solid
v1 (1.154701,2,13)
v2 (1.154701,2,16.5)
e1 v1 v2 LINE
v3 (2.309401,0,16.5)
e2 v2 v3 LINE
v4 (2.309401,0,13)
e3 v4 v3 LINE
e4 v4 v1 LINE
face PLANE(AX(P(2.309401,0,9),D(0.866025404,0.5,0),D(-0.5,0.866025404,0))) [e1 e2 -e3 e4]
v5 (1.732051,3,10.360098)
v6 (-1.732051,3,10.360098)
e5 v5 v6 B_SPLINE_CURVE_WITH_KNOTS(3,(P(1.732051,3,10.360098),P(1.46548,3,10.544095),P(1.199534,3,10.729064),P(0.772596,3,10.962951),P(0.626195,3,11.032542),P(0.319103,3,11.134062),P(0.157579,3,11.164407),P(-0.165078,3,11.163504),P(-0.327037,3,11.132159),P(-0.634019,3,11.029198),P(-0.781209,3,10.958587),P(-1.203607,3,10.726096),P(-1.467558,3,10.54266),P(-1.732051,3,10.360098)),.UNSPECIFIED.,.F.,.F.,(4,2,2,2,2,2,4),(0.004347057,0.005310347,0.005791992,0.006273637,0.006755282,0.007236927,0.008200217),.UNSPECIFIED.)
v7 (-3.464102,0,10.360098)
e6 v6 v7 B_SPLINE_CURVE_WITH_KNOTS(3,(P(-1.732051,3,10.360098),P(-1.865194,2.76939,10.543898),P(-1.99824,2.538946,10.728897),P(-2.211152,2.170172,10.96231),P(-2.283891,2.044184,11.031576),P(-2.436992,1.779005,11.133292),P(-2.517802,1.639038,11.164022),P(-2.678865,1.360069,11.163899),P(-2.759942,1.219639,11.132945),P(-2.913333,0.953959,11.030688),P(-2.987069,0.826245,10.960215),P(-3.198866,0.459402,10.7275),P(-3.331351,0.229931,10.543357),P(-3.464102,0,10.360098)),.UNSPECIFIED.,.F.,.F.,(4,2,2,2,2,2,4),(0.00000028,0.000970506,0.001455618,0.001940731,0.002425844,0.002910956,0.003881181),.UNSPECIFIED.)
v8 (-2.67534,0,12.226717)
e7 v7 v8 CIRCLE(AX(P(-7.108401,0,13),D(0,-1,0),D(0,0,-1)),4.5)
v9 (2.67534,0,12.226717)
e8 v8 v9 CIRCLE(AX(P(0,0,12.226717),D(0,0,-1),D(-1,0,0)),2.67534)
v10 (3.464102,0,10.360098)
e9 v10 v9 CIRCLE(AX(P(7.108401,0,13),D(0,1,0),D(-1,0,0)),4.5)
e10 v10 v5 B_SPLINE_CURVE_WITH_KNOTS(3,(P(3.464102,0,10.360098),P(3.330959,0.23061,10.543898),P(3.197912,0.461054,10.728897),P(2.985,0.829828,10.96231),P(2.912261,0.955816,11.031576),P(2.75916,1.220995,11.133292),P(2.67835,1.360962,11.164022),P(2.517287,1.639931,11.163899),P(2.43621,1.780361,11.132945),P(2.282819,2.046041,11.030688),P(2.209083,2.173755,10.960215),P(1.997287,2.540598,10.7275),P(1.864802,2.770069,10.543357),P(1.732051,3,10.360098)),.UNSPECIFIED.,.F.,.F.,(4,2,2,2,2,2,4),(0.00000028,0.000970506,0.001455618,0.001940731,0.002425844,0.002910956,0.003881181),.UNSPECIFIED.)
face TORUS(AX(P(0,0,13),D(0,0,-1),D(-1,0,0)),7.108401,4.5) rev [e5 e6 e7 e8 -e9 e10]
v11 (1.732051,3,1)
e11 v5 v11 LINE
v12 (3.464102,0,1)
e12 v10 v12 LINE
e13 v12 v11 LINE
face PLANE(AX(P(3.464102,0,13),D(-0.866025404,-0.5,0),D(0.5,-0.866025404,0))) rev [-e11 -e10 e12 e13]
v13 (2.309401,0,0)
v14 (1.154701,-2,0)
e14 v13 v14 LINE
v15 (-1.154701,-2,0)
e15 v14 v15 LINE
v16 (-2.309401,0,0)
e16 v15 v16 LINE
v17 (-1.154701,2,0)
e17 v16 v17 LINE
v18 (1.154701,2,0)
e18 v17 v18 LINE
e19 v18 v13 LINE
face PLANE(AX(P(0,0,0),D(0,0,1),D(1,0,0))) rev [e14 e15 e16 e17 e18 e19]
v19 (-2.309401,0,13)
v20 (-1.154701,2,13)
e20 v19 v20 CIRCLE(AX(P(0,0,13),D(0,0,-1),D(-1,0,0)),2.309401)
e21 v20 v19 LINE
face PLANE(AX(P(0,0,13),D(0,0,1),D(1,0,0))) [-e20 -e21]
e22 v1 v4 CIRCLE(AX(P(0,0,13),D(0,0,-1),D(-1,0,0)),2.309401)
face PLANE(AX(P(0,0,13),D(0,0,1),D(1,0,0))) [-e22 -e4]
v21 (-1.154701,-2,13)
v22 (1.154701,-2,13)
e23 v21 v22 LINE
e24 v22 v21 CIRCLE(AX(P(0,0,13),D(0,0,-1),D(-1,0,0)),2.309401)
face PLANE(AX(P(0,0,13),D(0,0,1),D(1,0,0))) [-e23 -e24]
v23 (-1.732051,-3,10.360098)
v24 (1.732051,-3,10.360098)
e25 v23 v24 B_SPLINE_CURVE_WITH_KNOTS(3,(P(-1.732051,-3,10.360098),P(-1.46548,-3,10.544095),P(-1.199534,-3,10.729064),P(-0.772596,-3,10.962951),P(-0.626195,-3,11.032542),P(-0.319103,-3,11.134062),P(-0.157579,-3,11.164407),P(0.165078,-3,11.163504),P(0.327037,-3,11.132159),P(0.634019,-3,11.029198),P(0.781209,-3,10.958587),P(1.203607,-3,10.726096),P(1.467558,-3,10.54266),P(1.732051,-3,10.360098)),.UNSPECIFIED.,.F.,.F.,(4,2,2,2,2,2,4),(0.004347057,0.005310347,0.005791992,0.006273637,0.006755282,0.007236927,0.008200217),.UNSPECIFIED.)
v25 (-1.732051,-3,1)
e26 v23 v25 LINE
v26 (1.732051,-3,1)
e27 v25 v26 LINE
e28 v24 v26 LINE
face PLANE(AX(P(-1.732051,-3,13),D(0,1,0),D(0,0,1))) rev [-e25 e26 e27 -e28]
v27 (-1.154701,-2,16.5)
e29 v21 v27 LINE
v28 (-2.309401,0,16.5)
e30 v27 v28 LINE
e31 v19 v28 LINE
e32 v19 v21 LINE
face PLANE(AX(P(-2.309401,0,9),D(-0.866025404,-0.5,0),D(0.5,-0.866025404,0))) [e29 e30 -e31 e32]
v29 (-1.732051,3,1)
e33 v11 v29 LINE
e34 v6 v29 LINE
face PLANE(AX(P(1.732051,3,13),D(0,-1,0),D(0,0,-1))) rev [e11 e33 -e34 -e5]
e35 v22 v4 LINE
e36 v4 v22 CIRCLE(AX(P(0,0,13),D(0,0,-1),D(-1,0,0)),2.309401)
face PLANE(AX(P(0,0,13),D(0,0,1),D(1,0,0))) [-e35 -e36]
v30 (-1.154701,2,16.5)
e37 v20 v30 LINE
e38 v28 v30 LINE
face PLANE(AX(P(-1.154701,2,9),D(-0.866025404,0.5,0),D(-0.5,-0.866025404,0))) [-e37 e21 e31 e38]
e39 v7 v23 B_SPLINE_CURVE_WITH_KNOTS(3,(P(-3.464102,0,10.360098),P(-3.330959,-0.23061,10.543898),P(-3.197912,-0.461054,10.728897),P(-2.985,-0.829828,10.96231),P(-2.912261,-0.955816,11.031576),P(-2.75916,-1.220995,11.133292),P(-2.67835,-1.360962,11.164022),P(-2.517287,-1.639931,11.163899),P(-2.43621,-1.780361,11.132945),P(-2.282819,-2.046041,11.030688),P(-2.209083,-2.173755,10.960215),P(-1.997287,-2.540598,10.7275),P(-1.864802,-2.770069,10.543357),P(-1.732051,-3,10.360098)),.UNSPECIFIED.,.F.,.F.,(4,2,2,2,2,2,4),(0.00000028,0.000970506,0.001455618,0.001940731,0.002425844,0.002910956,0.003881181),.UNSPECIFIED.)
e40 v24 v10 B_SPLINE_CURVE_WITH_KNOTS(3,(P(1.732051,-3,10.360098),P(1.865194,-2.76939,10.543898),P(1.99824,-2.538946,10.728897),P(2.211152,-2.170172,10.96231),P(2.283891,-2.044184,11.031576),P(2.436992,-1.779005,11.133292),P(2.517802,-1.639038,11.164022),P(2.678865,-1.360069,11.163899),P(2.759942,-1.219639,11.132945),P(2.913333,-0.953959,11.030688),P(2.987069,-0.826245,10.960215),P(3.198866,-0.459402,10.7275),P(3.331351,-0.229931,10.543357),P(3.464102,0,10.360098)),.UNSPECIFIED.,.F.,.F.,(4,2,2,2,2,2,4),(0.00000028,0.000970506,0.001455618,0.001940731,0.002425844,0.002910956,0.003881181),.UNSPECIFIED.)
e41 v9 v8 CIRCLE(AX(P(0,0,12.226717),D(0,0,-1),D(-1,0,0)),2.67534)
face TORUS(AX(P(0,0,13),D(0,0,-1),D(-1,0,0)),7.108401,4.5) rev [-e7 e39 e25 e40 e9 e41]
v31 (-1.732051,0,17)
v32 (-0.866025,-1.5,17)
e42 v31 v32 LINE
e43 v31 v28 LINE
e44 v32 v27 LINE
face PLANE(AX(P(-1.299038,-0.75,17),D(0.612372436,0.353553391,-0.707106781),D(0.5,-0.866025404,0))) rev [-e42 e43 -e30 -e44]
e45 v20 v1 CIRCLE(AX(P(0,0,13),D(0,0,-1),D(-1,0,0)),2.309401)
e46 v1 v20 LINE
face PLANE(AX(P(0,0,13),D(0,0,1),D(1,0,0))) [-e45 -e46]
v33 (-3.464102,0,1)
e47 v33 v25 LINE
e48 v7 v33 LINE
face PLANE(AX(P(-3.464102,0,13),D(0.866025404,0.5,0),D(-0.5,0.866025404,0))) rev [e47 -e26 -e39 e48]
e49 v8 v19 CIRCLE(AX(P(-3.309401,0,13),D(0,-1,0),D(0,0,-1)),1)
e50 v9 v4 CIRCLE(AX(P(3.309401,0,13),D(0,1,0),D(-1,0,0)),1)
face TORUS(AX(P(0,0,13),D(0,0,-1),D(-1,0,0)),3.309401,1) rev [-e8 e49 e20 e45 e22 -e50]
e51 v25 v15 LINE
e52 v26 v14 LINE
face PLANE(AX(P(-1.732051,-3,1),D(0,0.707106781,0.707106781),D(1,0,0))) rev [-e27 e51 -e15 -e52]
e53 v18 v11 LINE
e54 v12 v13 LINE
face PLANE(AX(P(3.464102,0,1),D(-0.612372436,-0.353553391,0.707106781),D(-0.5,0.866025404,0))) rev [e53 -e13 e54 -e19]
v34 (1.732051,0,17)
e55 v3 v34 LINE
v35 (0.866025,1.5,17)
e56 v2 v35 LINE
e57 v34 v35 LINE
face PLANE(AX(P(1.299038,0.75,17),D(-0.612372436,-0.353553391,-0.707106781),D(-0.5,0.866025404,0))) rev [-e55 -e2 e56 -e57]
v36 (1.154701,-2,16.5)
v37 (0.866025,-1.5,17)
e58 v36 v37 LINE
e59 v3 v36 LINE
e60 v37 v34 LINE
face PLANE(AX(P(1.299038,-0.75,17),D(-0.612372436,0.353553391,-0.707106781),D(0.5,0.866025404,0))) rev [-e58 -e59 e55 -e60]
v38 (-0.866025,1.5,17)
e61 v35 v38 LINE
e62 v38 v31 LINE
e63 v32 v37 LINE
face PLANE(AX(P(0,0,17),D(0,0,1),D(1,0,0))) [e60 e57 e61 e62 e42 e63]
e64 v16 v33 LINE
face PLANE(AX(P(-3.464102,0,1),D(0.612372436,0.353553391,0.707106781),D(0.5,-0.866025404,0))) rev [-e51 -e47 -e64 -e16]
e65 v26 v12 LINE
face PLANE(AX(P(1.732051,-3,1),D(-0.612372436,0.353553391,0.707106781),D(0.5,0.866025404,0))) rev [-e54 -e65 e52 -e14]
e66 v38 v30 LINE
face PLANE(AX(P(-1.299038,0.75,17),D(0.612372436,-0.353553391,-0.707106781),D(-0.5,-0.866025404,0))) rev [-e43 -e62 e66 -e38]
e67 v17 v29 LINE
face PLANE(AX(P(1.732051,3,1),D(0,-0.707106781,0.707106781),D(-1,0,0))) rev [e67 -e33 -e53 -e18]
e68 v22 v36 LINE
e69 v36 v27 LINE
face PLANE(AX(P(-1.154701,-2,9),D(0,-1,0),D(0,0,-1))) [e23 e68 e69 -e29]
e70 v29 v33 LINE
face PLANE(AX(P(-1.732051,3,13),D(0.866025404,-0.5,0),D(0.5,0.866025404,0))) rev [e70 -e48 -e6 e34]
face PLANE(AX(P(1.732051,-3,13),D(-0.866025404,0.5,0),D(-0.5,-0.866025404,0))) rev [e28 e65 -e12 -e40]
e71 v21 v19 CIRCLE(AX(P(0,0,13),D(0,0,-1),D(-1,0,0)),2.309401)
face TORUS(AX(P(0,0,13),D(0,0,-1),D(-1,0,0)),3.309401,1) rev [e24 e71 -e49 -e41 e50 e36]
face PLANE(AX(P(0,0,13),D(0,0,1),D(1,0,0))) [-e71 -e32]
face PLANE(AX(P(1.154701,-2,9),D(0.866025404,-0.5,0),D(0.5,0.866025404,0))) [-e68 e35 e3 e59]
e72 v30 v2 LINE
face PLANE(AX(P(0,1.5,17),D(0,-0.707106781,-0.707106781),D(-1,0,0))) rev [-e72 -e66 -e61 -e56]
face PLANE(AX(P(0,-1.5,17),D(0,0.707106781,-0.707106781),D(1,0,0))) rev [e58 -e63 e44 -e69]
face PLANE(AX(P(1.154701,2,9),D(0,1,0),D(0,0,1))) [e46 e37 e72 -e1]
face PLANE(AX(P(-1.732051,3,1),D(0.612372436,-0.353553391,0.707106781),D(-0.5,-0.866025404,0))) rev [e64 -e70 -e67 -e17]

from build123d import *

# Parameters (mm, degrees)
HEX_SHANK_6AF_X13_DEPTH   = 13
HEX_TIP_4AF_X4_DEPTH      = 4
HEX_TIP_4AF_X4_DEPTH_BACK = 4
TIP_CHAMFER_0_5_SIZE      = 0.5
SHANK_CHAMFER_1_SIZE      = 1


with BuildPart() as part:
    # Hex Shank Profile 6AF → Hex Shank 6AF x13 (new body)
    with BuildSketch(Plane.XY):
        Polygon((3.464101615, 0), (1.732050808, 3), (-1.732050808, 3), (-3.464101615, 0), (-1.732050808, -3), (1.732050808, -3), align=None)
    extrude(amount=HEX_SHANK_6AF_X13_DEPTH)

    # Hex Tip Profile 4AF → Hex Tip 4AF x4 (add, two sides: drawn at the far end of the back side and taken through both)
    with BuildSketch(Plane.XY.offset(13).offset(-HEX_TIP_4AF_X4_DEPTH_BACK)):
        Polygon((2.309401077, 0), (1.154700538, 2), (-1.154700538, 2), (-2.309401077, 0), (-1.154700538, -2), (1.154700538, -2), align=None)
    extrude(amount=HEX_TIP_4AF_X4_DEPTH + HEX_TIP_4AF_X4_DEPTH_BACK)

    # Neck Groove Profile → Neck Groove (revolve, cut)
    with BuildSketch(Plane(origin=(0, 0, 0), x_dir=(1, 0, 0), z_dir=(0, 1, 0)), mode=Mode.PRIVATE) as neck_groove_sk:
        with BuildLine():
            Line((3.464101615, -10.360098242), (3.464101615, -13))
            Line((3.464101615, -13), (2.309401077, -13))
            ThreePointArc((2.309401077, -13), (2.40550356, -12.572250915), (2.675339636, -12.226717329))
            ThreePointArc((2.675339636, -12.226717329), (2.963282684, -11.248431174), (3.464101615, -10.360098242))
        make_face()
    revolve(neck_groove_sk.sketch.rotate(Axis((0, 0, 0), (0, 0, 1)), 180), axis=Axis((0, 0, 0), (0, 0, 1)), mode=Mode.SUBTRACT)

    # Tip Chamfer 0.5
    tip_chamfer_0_5_edges = [part.edges().sort_by_distance(p)[0] for p in [
        (1.732050808, -1, 17),
        (1.732050808, 1, 17),
        (0, 2, 17),
        (-1.732050808, 1, 17),
        (-1.732050808, -1, 17),
        (0, -2, 17),
    ]]
    chamfer(tip_chamfer_0_5_edges, length=TIP_CHAMFER_0_5_SIZE)

    # Shank Chamfer 1
    shank_chamfer_1_edges = [part.edges().sort_by_distance(p)[0] for p in [
        (0, -3, 0),
        (-2.598076211, -1.5, 0),
        (-2.598076211, 1.5, 0),
        (0, 3, 0),
        (2.598076211, 1.5, 0),
        (2.598076211, -1.5, 0),
    ]]
    chamfer(shank_chamfer_1_edges, length=SHANK_CHAMFER_1_SIZE)


solid = part.part
